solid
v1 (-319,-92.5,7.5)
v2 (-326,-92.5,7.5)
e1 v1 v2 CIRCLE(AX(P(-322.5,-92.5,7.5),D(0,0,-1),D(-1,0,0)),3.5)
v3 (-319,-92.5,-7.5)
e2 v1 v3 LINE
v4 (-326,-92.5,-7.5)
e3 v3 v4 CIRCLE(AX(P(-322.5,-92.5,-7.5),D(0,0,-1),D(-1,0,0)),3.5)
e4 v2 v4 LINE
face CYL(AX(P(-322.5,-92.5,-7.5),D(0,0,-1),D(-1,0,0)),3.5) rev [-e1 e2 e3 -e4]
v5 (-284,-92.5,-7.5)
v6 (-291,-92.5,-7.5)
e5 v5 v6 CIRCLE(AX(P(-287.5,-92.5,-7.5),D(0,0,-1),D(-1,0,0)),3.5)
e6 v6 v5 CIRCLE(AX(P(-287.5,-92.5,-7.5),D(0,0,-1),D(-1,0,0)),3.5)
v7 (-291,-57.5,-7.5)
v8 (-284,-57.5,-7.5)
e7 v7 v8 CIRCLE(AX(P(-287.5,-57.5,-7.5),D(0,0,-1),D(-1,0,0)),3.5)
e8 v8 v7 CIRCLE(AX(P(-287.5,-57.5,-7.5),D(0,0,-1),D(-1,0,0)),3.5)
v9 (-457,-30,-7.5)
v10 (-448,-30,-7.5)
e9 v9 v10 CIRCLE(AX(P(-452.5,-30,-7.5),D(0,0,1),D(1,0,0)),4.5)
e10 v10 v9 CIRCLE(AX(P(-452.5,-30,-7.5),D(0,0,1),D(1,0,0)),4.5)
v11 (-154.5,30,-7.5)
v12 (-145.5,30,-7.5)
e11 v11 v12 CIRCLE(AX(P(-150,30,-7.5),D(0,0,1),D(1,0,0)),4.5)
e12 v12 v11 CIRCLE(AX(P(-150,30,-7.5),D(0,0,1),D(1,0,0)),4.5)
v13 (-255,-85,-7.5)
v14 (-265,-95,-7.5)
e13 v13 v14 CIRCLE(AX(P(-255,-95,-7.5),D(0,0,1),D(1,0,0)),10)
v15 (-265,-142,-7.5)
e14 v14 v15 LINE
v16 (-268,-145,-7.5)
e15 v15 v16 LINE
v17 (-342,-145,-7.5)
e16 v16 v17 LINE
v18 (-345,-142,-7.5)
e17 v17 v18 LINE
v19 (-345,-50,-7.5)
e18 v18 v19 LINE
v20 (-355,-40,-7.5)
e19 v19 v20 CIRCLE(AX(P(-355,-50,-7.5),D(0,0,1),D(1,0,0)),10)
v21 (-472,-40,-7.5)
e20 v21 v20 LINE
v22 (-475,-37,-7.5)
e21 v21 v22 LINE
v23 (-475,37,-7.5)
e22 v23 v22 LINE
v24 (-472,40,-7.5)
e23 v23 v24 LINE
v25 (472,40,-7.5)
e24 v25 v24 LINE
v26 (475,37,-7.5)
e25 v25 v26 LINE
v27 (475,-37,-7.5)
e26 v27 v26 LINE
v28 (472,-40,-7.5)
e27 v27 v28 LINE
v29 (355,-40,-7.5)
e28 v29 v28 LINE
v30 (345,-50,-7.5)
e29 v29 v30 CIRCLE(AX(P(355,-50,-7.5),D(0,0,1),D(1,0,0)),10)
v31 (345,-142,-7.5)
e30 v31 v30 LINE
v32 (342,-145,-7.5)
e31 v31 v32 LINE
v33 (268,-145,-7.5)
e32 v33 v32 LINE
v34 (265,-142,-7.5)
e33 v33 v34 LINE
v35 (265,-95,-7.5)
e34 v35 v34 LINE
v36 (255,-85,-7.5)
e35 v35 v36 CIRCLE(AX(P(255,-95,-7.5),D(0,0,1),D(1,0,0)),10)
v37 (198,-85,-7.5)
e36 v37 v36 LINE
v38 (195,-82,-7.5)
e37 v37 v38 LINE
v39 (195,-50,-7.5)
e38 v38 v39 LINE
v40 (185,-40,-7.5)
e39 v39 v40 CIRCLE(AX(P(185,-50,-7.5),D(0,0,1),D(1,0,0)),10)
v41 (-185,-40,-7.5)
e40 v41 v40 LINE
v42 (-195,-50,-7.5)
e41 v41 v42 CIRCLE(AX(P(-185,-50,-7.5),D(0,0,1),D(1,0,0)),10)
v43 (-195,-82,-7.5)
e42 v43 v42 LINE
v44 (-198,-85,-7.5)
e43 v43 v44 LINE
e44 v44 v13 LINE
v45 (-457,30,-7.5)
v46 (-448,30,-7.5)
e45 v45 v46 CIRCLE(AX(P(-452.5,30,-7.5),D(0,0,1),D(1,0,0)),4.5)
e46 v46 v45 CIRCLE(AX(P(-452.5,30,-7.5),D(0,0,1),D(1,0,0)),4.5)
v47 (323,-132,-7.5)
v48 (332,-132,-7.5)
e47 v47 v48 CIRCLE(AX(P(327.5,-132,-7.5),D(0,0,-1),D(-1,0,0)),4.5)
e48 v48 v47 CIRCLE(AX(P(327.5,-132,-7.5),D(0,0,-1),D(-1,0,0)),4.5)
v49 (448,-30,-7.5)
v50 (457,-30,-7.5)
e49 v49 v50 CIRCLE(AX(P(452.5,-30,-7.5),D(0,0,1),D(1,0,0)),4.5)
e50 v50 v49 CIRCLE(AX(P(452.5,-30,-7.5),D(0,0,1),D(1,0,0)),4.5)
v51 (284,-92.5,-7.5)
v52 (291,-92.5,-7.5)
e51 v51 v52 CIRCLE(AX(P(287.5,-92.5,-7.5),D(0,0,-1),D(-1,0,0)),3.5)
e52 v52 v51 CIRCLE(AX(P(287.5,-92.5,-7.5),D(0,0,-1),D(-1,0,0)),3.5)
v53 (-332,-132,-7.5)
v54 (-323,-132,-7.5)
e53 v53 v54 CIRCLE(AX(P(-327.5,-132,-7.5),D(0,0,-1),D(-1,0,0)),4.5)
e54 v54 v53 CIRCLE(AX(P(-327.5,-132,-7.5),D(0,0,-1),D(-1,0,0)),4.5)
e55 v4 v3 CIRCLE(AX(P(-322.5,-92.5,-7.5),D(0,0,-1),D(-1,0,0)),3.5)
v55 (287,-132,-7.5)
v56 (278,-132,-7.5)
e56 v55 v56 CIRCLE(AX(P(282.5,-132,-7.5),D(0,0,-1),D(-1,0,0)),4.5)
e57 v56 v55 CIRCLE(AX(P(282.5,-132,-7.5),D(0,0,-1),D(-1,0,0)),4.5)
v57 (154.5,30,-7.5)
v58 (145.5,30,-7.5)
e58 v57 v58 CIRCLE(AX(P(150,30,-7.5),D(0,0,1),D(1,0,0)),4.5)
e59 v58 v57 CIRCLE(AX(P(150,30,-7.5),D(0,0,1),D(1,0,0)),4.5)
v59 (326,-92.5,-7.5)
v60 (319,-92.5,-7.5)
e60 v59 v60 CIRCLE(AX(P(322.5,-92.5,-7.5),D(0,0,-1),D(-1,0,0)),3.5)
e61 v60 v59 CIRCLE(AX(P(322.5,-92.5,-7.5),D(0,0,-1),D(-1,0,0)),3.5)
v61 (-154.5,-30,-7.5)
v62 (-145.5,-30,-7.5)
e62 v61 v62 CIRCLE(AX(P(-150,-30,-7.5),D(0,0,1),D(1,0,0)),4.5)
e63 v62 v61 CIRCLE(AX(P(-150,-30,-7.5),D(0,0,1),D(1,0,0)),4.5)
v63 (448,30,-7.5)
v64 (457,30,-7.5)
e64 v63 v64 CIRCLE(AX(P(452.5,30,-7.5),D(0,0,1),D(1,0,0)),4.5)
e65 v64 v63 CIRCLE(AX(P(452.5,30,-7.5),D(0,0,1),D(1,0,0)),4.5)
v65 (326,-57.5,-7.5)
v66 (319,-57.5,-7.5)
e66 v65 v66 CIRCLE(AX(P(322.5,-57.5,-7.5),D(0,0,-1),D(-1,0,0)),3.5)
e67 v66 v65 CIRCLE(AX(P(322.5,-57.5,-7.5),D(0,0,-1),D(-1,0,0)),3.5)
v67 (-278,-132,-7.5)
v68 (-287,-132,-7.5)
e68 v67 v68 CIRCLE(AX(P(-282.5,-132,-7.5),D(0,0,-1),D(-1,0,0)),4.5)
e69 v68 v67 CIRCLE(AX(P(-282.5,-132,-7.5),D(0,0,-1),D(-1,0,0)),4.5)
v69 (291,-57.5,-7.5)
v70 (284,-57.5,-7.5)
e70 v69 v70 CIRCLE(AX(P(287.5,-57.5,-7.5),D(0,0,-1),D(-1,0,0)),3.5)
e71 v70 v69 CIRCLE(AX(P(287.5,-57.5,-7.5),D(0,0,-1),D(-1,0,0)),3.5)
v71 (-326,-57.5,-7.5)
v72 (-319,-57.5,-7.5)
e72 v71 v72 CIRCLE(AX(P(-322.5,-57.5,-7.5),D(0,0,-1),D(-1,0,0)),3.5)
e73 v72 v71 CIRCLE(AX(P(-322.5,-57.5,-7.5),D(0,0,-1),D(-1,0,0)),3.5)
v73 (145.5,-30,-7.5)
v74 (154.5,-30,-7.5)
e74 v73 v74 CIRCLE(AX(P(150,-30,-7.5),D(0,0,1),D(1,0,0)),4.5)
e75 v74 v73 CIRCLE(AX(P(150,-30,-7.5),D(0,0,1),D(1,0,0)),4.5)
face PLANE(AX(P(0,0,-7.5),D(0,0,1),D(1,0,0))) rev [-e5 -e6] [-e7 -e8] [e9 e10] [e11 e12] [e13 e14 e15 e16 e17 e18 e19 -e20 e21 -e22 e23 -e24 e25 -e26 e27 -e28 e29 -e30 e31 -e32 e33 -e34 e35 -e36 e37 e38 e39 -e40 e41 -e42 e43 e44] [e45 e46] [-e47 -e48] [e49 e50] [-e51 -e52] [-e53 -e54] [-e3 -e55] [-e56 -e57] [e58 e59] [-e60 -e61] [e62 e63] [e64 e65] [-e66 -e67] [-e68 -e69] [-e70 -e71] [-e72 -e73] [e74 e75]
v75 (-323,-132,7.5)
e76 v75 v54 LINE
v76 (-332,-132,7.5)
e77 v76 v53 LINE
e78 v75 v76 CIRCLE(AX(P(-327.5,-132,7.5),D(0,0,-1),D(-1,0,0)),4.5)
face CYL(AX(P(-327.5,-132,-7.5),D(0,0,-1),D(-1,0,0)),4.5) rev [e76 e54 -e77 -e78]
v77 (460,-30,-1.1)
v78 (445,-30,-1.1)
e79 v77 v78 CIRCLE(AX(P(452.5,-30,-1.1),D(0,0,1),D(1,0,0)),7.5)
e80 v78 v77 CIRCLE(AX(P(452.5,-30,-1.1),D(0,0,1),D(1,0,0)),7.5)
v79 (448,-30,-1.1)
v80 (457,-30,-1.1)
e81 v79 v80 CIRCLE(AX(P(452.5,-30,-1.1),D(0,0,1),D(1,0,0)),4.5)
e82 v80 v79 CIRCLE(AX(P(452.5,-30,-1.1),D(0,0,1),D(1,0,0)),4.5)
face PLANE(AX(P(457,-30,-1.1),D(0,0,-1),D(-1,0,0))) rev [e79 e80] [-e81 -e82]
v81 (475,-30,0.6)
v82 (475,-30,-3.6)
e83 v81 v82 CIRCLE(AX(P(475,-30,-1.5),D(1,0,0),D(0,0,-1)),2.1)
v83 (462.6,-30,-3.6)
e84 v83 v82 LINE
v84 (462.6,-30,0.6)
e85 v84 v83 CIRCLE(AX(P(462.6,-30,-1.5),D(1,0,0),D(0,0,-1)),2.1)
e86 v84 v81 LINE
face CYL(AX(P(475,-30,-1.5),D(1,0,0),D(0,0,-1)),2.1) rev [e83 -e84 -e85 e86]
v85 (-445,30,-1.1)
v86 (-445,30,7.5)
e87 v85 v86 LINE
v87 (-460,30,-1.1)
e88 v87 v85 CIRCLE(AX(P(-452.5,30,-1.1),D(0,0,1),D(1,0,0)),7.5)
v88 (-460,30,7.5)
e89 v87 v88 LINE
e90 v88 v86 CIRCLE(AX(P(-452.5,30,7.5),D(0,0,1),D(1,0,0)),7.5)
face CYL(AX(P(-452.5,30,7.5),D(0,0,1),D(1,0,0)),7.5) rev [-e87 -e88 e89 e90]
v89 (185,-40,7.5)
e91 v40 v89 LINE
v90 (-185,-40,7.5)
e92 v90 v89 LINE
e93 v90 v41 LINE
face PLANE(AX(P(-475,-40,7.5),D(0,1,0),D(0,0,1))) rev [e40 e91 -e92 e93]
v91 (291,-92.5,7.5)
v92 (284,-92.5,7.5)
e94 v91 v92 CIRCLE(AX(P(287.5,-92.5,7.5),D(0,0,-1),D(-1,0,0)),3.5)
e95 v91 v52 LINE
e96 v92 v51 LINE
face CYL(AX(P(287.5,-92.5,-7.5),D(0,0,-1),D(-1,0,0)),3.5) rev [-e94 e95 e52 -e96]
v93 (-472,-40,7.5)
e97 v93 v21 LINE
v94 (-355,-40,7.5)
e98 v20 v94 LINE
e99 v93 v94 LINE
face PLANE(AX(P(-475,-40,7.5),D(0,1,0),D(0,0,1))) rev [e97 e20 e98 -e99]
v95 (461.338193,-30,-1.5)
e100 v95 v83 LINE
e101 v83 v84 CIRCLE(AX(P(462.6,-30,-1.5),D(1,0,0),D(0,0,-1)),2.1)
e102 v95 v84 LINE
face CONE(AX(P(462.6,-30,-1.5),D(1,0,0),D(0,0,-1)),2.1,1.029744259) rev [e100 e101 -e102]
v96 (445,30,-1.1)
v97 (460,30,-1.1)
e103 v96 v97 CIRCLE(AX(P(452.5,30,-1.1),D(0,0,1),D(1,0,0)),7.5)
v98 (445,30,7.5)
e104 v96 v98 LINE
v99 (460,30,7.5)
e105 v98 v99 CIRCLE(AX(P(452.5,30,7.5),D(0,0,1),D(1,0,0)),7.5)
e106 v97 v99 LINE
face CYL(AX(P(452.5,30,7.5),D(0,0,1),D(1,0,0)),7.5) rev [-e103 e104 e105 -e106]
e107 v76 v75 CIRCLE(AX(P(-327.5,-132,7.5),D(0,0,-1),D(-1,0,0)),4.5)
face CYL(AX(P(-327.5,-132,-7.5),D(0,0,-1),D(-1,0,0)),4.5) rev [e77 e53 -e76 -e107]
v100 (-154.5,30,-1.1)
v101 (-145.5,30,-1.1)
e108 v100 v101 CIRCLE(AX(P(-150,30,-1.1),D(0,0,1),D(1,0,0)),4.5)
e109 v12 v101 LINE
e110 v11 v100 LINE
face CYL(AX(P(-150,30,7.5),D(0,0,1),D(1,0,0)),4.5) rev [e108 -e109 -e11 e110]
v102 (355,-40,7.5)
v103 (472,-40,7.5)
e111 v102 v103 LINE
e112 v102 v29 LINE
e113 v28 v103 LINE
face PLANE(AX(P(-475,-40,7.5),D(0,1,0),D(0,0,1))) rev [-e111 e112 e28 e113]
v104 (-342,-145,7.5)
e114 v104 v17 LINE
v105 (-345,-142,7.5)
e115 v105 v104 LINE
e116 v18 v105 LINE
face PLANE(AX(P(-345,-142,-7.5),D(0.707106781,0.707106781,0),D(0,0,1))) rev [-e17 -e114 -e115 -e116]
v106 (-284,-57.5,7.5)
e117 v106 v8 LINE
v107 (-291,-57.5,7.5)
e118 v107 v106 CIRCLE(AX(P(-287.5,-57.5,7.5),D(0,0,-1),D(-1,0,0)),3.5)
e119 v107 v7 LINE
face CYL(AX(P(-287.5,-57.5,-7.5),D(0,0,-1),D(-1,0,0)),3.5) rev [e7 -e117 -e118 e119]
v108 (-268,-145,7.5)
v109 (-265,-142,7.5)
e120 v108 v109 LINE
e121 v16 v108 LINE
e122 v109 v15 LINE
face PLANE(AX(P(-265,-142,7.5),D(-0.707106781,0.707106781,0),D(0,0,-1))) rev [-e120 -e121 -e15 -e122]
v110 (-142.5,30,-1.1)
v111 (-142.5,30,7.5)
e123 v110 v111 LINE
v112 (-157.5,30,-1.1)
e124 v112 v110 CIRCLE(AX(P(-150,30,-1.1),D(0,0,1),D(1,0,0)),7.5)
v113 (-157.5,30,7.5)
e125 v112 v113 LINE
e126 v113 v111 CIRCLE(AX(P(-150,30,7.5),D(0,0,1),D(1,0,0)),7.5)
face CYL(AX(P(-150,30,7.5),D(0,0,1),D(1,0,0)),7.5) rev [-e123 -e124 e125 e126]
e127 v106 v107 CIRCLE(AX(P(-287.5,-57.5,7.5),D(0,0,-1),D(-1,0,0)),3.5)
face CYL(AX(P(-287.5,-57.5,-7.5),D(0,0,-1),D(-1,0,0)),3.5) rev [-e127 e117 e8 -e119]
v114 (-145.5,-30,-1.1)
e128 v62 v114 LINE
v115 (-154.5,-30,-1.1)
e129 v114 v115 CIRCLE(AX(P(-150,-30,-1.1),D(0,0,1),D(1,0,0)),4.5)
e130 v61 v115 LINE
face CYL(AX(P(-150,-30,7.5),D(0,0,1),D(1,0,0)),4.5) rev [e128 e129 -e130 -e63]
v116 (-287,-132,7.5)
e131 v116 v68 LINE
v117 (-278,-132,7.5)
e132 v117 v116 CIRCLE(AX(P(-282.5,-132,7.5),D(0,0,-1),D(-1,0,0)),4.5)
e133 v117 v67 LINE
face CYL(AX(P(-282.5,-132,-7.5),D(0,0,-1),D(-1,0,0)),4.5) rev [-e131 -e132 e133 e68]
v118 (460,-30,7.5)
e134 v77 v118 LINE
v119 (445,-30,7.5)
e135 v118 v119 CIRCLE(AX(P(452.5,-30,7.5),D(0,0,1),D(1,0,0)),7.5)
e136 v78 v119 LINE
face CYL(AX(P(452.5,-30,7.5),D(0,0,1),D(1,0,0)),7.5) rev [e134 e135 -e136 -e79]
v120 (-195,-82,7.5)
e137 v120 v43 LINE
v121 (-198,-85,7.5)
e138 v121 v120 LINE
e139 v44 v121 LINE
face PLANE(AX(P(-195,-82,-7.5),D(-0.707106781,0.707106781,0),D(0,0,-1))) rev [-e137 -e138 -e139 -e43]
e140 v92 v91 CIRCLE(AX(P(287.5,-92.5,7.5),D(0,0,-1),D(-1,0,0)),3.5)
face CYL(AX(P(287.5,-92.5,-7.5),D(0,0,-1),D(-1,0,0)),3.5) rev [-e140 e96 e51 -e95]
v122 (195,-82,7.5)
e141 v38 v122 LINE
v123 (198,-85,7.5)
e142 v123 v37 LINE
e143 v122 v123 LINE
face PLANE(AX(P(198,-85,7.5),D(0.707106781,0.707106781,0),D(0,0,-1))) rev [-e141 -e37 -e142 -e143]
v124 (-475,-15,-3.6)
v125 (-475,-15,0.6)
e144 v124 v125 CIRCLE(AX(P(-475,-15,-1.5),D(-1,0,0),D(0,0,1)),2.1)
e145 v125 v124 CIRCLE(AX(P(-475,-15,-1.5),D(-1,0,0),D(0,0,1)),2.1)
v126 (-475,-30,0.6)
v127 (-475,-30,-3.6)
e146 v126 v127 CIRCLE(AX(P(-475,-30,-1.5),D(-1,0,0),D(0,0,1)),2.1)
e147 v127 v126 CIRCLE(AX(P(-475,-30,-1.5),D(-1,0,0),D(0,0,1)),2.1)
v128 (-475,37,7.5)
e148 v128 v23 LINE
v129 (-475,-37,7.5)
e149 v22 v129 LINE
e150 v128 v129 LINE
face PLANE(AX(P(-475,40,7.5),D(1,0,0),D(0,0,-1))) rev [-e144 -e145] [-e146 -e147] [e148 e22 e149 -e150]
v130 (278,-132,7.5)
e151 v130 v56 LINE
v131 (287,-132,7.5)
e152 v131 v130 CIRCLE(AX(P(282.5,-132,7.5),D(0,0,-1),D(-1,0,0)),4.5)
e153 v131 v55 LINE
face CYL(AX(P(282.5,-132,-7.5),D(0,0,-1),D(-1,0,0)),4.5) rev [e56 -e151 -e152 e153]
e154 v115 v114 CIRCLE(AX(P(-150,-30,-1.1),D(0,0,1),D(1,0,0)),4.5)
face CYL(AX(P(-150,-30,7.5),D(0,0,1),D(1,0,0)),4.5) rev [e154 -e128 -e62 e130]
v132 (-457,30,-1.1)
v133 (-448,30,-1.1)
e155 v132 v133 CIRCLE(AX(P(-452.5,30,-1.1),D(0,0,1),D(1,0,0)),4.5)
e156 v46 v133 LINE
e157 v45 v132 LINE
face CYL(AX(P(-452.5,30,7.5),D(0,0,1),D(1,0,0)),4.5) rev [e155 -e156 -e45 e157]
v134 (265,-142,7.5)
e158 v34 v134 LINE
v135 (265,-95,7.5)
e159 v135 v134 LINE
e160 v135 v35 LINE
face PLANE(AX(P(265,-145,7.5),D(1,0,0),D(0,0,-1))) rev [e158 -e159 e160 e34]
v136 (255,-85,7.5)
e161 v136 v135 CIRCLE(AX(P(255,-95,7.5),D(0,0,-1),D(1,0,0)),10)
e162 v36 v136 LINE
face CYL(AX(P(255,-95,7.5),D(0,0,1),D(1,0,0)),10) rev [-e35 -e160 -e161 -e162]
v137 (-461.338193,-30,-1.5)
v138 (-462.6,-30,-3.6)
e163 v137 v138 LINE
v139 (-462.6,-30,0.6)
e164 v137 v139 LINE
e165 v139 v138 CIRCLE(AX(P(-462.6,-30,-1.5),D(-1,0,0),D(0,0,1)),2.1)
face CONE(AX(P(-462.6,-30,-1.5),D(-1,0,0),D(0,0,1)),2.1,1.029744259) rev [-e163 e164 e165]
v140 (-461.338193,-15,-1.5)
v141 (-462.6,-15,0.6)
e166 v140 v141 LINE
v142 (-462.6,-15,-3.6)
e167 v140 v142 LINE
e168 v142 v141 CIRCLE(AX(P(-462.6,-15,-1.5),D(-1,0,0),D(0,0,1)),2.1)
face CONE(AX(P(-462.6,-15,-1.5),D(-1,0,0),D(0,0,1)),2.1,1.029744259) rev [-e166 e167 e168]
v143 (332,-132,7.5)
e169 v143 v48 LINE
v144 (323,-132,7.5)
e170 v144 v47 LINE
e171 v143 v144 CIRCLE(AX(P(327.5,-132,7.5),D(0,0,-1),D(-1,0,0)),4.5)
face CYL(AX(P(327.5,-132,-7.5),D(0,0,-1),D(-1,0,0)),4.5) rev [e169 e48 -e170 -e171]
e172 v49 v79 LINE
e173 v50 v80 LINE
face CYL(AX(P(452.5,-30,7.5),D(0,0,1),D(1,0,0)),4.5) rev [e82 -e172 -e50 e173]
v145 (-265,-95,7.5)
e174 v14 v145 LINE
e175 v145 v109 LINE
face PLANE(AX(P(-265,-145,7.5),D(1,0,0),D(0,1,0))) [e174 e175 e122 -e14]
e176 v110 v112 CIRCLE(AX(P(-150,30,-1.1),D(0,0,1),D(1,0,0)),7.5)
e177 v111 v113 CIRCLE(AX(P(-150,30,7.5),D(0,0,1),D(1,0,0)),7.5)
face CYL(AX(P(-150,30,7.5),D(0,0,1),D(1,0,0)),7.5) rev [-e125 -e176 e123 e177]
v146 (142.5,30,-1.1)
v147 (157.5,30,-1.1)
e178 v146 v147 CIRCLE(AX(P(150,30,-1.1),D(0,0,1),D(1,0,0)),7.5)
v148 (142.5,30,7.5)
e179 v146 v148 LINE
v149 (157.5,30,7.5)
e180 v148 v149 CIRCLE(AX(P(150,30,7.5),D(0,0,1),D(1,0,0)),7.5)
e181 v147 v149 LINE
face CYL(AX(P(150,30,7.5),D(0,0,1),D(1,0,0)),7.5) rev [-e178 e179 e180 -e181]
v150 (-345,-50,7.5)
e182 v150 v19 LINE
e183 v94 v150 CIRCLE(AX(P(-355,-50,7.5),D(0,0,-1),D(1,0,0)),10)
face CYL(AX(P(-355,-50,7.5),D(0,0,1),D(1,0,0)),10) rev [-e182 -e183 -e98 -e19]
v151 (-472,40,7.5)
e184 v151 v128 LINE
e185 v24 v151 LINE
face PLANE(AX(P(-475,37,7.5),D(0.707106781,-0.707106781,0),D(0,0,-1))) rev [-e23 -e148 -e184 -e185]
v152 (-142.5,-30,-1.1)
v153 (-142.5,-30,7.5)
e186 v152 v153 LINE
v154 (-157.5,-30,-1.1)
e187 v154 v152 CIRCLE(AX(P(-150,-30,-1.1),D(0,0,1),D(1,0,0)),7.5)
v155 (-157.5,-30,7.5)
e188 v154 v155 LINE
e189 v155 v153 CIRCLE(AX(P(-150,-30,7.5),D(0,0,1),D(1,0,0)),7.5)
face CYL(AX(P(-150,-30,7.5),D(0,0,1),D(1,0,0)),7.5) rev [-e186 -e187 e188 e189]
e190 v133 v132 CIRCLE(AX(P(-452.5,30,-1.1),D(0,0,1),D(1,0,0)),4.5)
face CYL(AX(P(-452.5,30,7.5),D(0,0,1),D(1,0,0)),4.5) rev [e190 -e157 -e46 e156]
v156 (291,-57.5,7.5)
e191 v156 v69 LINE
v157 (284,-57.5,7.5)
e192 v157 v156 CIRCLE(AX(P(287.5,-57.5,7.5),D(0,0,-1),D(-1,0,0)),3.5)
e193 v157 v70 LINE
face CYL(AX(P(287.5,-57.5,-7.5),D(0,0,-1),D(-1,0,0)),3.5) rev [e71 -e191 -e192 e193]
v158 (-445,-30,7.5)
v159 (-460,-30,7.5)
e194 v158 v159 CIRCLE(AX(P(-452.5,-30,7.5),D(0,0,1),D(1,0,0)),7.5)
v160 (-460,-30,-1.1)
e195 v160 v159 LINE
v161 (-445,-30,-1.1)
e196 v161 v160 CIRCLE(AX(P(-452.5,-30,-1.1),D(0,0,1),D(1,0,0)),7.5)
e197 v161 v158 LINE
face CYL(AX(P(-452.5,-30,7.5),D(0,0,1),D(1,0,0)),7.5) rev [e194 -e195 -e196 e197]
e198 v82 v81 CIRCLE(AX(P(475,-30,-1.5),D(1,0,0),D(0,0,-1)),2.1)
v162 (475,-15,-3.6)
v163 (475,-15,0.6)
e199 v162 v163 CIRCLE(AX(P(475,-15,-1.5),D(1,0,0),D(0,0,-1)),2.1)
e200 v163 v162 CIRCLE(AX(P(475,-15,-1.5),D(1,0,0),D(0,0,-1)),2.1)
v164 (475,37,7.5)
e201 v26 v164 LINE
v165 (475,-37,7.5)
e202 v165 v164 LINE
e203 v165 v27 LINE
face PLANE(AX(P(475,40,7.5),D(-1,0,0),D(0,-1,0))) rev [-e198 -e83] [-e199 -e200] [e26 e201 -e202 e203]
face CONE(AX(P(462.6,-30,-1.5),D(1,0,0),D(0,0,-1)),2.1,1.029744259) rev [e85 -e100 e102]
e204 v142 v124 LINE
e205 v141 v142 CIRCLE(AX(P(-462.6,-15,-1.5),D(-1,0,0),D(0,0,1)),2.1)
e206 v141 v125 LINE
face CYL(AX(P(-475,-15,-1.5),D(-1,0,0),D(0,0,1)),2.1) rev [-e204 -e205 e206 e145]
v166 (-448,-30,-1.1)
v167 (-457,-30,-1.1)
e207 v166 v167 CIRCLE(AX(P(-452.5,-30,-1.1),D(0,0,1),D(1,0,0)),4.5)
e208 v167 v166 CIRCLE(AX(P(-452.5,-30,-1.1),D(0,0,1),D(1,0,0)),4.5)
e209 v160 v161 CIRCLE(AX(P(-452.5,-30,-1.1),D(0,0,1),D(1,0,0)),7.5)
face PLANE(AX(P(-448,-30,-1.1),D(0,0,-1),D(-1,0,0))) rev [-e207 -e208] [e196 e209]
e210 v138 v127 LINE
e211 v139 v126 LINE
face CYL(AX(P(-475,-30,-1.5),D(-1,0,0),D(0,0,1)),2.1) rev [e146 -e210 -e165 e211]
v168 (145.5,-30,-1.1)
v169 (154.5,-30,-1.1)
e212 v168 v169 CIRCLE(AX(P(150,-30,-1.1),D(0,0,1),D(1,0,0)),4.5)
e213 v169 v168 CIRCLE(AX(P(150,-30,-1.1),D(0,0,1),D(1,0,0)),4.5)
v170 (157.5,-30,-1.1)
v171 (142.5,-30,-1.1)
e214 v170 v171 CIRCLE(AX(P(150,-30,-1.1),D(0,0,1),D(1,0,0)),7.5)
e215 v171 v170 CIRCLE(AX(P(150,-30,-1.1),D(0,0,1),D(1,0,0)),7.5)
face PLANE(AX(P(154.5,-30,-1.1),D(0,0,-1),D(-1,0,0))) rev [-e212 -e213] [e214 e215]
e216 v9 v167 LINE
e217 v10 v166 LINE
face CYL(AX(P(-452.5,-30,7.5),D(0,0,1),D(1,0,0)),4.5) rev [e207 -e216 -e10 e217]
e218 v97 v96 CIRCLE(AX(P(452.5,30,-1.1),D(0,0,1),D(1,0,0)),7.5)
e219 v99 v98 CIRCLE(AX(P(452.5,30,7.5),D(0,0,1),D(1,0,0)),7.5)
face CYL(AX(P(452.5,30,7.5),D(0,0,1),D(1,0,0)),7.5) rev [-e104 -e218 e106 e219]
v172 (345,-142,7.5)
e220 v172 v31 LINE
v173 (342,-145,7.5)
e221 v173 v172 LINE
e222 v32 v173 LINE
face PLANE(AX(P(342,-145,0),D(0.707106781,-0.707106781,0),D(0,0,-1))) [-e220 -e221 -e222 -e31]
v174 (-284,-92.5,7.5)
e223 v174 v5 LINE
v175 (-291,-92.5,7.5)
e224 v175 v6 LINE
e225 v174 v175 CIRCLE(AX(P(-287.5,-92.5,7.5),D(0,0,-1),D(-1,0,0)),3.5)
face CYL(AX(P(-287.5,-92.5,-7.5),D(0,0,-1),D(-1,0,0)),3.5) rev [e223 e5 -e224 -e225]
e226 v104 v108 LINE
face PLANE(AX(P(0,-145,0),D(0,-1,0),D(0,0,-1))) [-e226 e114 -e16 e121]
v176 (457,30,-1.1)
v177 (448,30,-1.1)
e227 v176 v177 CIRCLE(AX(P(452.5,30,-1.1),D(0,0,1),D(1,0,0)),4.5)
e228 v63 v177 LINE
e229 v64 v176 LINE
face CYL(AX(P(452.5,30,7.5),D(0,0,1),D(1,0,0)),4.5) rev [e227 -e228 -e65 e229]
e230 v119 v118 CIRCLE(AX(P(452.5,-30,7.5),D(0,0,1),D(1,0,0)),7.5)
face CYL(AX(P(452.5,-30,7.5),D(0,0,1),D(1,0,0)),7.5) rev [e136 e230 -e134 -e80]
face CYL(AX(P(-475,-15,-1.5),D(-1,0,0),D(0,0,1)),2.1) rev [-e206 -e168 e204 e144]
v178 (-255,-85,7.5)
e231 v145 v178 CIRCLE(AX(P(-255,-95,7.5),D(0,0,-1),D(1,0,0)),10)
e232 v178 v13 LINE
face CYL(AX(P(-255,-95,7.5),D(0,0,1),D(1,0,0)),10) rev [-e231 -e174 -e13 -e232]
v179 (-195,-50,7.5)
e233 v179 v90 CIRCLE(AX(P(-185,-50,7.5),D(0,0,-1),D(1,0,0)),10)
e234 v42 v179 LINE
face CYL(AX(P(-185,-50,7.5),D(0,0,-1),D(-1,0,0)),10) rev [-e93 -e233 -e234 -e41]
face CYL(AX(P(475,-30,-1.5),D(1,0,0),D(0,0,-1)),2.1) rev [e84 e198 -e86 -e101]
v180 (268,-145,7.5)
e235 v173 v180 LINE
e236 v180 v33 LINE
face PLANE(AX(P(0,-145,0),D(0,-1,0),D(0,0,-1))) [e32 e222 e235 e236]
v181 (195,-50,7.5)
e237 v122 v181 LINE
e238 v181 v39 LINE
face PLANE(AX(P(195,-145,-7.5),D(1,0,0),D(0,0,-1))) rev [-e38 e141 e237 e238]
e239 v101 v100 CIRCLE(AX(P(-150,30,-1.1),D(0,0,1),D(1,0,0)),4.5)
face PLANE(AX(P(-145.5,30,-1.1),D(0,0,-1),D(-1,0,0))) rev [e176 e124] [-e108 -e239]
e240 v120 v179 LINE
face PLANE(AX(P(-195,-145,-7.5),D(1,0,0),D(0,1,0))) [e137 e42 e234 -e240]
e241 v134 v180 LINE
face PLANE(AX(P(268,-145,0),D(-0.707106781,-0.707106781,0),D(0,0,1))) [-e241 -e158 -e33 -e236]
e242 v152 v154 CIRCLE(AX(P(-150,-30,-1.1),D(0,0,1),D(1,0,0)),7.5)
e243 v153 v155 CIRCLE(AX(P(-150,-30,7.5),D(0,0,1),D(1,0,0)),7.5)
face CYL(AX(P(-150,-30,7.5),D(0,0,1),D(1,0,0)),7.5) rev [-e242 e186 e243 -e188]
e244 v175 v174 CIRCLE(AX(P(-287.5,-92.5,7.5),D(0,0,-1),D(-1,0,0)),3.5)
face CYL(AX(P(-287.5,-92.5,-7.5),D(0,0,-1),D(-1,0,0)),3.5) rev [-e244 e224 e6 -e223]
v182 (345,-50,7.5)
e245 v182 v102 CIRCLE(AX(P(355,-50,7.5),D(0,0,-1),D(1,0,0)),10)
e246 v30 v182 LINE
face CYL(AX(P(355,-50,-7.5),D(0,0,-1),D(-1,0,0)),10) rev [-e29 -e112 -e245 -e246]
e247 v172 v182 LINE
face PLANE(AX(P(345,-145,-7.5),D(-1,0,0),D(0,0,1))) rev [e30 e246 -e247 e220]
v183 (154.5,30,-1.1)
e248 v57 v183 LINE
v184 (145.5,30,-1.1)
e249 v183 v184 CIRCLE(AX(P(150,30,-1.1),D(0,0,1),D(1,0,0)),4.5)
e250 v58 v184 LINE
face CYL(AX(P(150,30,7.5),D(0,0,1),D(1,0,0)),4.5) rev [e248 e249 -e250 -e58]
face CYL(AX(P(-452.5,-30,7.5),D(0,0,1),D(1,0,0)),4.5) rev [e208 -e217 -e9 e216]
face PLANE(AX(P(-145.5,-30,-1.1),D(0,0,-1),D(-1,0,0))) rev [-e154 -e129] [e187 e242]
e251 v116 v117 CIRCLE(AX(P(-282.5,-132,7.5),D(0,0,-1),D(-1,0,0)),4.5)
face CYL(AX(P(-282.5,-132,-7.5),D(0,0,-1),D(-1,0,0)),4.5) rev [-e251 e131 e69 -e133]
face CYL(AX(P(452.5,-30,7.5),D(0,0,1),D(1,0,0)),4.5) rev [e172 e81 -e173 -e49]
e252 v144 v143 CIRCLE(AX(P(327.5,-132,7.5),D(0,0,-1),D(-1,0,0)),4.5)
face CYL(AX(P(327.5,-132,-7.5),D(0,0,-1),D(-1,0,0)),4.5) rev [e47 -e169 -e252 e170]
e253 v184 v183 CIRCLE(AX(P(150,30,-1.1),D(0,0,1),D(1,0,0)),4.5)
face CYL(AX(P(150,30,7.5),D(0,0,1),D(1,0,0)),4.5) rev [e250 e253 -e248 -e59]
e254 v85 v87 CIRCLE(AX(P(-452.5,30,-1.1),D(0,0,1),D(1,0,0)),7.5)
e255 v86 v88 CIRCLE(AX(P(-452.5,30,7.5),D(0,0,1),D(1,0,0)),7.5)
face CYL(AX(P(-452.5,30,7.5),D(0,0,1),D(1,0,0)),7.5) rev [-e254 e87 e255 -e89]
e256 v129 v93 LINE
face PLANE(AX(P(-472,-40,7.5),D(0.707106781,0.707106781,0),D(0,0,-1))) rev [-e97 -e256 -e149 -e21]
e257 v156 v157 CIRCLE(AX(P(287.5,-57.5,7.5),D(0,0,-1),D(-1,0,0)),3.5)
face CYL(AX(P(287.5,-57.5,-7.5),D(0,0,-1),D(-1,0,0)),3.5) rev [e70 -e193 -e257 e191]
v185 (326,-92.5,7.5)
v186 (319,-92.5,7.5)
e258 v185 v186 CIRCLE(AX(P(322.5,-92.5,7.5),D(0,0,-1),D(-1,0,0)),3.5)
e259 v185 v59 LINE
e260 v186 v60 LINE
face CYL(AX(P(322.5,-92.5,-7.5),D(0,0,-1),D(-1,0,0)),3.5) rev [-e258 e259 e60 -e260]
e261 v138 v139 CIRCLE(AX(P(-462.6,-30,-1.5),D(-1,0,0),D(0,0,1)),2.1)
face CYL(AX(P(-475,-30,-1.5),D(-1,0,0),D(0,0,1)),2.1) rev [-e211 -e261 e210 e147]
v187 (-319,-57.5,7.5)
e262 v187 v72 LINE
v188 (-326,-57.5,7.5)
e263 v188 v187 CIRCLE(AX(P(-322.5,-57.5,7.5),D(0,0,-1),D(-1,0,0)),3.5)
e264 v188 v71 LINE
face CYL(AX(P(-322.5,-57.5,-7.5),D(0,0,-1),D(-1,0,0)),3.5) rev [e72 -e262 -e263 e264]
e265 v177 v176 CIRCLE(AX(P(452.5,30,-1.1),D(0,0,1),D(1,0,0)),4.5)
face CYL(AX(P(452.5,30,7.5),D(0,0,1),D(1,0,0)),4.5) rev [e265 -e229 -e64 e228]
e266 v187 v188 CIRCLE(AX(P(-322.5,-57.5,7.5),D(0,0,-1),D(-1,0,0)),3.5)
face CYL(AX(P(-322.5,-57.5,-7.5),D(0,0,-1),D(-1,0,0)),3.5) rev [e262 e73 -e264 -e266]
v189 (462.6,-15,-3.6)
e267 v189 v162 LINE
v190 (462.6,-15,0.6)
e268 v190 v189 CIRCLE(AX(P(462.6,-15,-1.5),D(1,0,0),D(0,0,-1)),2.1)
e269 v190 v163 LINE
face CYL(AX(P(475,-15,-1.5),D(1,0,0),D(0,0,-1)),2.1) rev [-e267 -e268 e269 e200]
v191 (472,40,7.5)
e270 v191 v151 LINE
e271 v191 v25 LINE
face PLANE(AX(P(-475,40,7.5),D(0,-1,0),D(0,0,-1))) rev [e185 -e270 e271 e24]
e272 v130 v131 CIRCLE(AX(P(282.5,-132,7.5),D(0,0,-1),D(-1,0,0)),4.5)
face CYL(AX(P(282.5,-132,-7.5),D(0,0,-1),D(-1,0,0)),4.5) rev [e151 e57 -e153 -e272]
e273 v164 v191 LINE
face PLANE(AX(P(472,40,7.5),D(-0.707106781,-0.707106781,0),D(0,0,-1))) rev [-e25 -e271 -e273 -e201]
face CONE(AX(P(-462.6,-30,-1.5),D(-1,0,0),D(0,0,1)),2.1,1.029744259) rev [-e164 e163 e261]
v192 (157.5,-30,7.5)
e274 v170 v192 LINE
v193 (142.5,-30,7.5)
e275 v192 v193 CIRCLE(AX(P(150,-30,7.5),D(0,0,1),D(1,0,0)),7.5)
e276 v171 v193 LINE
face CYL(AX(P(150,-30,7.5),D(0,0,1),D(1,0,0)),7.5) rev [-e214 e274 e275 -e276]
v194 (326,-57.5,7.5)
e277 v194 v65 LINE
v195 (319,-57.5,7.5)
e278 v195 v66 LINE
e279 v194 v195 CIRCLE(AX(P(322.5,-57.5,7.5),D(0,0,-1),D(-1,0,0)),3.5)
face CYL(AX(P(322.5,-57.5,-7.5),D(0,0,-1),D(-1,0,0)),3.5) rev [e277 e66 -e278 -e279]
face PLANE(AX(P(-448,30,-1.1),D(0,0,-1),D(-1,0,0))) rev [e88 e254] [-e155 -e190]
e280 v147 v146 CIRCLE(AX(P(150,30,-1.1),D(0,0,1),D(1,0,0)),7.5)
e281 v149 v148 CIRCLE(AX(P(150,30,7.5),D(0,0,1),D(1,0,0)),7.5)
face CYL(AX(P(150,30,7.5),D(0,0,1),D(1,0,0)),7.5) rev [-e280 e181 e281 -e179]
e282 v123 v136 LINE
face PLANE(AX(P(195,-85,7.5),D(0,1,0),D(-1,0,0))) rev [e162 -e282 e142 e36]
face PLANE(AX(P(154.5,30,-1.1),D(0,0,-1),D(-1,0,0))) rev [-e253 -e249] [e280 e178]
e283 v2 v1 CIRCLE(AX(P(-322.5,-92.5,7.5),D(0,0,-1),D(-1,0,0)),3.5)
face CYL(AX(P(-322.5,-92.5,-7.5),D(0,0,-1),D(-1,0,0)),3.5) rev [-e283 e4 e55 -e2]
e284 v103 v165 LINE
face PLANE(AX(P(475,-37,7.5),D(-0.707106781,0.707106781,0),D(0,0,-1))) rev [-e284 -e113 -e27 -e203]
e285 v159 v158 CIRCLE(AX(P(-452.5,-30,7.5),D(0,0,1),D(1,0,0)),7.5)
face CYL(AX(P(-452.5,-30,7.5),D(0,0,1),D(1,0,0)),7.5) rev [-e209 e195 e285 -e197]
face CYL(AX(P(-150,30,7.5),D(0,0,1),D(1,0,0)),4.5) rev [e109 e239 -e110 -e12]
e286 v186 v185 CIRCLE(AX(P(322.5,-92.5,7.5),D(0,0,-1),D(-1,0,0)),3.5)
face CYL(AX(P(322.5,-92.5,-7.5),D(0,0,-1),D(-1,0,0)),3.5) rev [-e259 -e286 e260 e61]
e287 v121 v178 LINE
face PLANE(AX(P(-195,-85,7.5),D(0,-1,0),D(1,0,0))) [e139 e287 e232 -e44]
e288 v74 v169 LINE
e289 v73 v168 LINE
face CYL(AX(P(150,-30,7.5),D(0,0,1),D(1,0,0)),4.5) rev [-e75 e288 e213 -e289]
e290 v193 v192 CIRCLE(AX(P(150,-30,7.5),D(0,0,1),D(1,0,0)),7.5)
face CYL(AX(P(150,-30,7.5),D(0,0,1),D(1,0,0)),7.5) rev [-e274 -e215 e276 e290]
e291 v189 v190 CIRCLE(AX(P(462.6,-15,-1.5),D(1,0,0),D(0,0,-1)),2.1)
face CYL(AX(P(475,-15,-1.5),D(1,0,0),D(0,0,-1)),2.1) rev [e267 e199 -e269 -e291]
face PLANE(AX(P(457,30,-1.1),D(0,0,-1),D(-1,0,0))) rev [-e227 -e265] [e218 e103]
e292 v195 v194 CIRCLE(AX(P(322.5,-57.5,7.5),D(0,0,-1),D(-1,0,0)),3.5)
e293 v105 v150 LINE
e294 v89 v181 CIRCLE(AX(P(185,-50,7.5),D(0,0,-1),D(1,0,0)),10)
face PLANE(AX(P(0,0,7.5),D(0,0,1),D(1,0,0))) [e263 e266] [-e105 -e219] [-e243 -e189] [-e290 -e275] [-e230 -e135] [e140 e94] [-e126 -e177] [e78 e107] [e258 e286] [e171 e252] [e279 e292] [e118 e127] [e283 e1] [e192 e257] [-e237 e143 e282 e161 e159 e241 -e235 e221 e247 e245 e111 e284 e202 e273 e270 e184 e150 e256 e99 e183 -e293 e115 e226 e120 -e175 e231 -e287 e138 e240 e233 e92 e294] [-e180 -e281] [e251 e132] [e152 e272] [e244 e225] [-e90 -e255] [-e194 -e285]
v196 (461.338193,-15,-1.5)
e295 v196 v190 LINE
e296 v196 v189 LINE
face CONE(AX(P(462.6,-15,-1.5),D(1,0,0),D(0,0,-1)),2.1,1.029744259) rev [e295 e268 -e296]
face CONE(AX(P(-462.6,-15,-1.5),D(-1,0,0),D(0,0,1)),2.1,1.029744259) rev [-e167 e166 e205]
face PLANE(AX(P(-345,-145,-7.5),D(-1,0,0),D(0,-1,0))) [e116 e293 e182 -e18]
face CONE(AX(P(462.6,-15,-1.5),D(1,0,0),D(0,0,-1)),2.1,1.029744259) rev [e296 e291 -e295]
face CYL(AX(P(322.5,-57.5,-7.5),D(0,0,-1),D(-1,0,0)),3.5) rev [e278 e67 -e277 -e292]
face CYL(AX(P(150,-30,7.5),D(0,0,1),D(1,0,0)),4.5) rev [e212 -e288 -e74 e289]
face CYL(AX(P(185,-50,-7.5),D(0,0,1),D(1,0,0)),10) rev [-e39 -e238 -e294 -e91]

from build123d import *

# Parameters (mm, degrees)
SKETCH_1_W                   = 950
SKETCH_1_H                   = 80
EXTRUDE_1_DEPTH              = 7.5
HOLE_WIZARD_M8_1_D           = 9
HOLE_WIZARD_M8_1_CBORE_D     = 15
HOLE_WIZARD_M8_1_CBORE_DEPTH = 8.6
CHAMFER_1_SIZE               = 3
SKETCH_7_W                   = 150
SKETCH_7_H                   = 15
EXTRUDE_2_DEPTH              = 105
FILLET_1_R                   = 10
HOLE_WIZARD_M6_1_D           = 7
HOLE_WIZARD_9_0_9_1_D        = 9
HOLE_WIZARD_M5_1_D           = 4.2
HOLE_WIZARD_M5_1_DEPTH       = 12.4
HOLE_WIZARD_M5_1_TIP         = 1.2618073
HOLE_WIZARD_M5_2_D           = 4.2
HOLE_WIZARD_M5_2_DEPTH       = 12.4
HOLE_WIZARD_M5_2_TIP         = 1.2618073
SKETCH_17_W                  = 70
SKETCH_17_H                  = 60
CUT_EXTRUDE_1_DEPTH          = 497.865172859
FILLET_2_R                   = 10
CHAMFER_3_SIZE               = 3


with BuildPart() as part:
    # 草图1 → 凸台-拉伸1 (new, symmetric)
    with BuildSketch(Plane.XY):
        Rectangle(SKETCH_1_W, SKETCH_1_H)
    extrude(amount=EXTRUDE_1_DEPTH, both=True)

    # M8 六角凹头螺钉的柱形沉头孔1 (through all)
    with Locations(Plane.XY.offset(7.5)):
        with Locations((452.5, -30), (452.5, 30), (150, -30), (150, 30), (-452.5, 30), (-452.5, -30), (-150, 30), (-150, -30)):
            CounterBoreHole(HOLE_WIZARD_M8_1_D / 2, HOLE_WIZARD_M8_1_CBORE_D / 2, HOLE_WIZARD_M8_1_CBORE_DEPTH)

    # 倒角1
    chamfer_1_edges = [part.edges().sort_by_distance(p)[0] for p in [
        (475, -40, 0),
        (-475, -40, 0),
        (-475, 40, 0),
        (475, 40, 0),
    ]]
    chamfer(chamfer_1_edges, length=CHAMFER_1_SIZE)

    # 草图7 → 凸台-拉伸2 (add)
    with BuildSketch(Plane.XZ.offset(40)):
        with Locations((270, 0)):
            Rectangle(SKETCH_7_W, SKETCH_7_H)
    extrude_2 = extrude(amount=EXTRUDE_2_DEPTH)

    # 镜向1: 凸台-拉伸2 across plane
    add(extrude_2.mirror(Plane(origin=(0, 0, 0), x_dir=(0, 0, 1), z_dir=(1, 0, 0))))

    # 圆角1
    fillet_1_edges = [part.edges().sort_by_distance(p)[0] for p in [
        (-345, -40, 0),
        (-195, -40, 0),
        (195, -40, 0),
        (345, -40, 0),
    ]]
    fillet(fillet_1_edges, radius=FILLET_1_R)

    # M6 六角凹头螺钉的柱形沉头孔1 (through all)
    with Locations(Plane(origin=(0, 0, -7.5), x_dir=(-1, 0, 0), z_dir=(0, 0, -1))):
        with Locations((-287.5, -92.5), (-287.5, -57.5), (-322.5, -57.5), (-322.5, -92.5)):
            hole_wizard_m6_1 = Hole(HOLE_WIZARD_M6_1_D / 2)

    # Ø9.0 (9) 直径孔1 (through all)
    with Locations(Plane(origin=(0, 0, -7.5), x_dir=(-1, 0, 0), z_dir=(0, 0, -1))):
        with Locations((-282.5, -132), (-327.5, -132)):
            hole_wizard_9_0_9_1 = Hole(HOLE_WIZARD_9_0_9_1_D / 2)

    # 镜向2: M6 六角凹头螺钉的柱形沉头孔1, Ø9.0 (9) 直径孔1 across plane
    add(hole_wizard_m6_1.mirror(Plane(origin=(0, 0, 0), x_dir=(0, 0, 1), z_dir=(1, 0, 0))), mode=Mode.SUBTRACT)
    add(hole_wizard_9_0_9_1.mirror(Plane(origin=(0, 0, 0), x_dir=(0, 0, 1), z_dir=(1, 0, 0))), mode=Mode.SUBTRACT)

    # M5 螺纹孔1
    with Locations(Plane.ZY.offset(475)):
        with Locations((-1.5, -30), (-1.5, -15)):
            Hole(HOLE_WIZARD_M5_1_D / 2, depth=HOLE_WIZARD_M5_1_DEPTH)
            with Locations((0, 0, -(HOLE_WIZARD_M5_1_DEPTH + HOLE_WIZARD_M5_1_TIP / 2))):  # 118° drill point
                Cone(0, HOLE_WIZARD_M5_1_D / 2, HOLE_WIZARD_M5_1_TIP, mode=Mode.SUBTRACT)

    # M5 螺纹孔2
    with Locations(Plane(origin=(475, 0, 0), x_dir=(0, 0, -1), z_dir=(1, 0, 0))):
        with Locations((1.5, -15), (1.5, -30)):
            Hole(HOLE_WIZARD_M5_2_D / 2, depth=HOLE_WIZARD_M5_2_DEPTH)
            with Locations((0, 0, -(HOLE_WIZARD_M5_2_DEPTH + HOLE_WIZARD_M5_2_TIP / 2))):  # 118° drill point
                Cone(0, HOLE_WIZARD_M5_2_D / 2, HOLE_WIZARD_M5_2_TIP, mode=Mode.SUBTRACT)

    # 草图17 → 切除-拉伸1 (cut, through all)
    with BuildSketch(Plane(origin=(0, 0, -7.5), x_dir=(-1, 0, 0), z_dir=(0, 0, -1))):
        with Locations((-230, -115)):
            Rectangle(SKETCH_17_W, SKETCH_17_H)
    cut_extrude_1 = extrude(amount=-CUT_EXTRUDE_1_DEPTH, mode=Mode.SUBTRACT)

    # 镜向3: 切除-拉伸1 across plane
    add(cut_extrude_1.mirror(Plane(origin=(0, 0, 0), x_dir=(0, 0, 1), z_dir=(1, 0, 0))), mode=Mode.SUBTRACT)

    # 圆角2
    fillet_2_edges = [part.edges().sort_by_distance(p)[0] for p in [
        (265, -85, 0),
        (-265, -85, 0),
    ]]
    fillet(fillet_2_edges, radius=FILLET_2_R)

    # 倒角3
    chamfer_3_edges = [part.edges().sort_by_distance(p)[0] for p in [
        (-345, -145, 0),
        (-265, -145, 0),
        (-195, -85, 0),
        (195, -85, 0),
        (265, -145, 0),
        (345, -145, 0),
    ]]
    chamfer(chamfer_3_edges, length=CHAMFER_3_SIZE)


solid = part.part
